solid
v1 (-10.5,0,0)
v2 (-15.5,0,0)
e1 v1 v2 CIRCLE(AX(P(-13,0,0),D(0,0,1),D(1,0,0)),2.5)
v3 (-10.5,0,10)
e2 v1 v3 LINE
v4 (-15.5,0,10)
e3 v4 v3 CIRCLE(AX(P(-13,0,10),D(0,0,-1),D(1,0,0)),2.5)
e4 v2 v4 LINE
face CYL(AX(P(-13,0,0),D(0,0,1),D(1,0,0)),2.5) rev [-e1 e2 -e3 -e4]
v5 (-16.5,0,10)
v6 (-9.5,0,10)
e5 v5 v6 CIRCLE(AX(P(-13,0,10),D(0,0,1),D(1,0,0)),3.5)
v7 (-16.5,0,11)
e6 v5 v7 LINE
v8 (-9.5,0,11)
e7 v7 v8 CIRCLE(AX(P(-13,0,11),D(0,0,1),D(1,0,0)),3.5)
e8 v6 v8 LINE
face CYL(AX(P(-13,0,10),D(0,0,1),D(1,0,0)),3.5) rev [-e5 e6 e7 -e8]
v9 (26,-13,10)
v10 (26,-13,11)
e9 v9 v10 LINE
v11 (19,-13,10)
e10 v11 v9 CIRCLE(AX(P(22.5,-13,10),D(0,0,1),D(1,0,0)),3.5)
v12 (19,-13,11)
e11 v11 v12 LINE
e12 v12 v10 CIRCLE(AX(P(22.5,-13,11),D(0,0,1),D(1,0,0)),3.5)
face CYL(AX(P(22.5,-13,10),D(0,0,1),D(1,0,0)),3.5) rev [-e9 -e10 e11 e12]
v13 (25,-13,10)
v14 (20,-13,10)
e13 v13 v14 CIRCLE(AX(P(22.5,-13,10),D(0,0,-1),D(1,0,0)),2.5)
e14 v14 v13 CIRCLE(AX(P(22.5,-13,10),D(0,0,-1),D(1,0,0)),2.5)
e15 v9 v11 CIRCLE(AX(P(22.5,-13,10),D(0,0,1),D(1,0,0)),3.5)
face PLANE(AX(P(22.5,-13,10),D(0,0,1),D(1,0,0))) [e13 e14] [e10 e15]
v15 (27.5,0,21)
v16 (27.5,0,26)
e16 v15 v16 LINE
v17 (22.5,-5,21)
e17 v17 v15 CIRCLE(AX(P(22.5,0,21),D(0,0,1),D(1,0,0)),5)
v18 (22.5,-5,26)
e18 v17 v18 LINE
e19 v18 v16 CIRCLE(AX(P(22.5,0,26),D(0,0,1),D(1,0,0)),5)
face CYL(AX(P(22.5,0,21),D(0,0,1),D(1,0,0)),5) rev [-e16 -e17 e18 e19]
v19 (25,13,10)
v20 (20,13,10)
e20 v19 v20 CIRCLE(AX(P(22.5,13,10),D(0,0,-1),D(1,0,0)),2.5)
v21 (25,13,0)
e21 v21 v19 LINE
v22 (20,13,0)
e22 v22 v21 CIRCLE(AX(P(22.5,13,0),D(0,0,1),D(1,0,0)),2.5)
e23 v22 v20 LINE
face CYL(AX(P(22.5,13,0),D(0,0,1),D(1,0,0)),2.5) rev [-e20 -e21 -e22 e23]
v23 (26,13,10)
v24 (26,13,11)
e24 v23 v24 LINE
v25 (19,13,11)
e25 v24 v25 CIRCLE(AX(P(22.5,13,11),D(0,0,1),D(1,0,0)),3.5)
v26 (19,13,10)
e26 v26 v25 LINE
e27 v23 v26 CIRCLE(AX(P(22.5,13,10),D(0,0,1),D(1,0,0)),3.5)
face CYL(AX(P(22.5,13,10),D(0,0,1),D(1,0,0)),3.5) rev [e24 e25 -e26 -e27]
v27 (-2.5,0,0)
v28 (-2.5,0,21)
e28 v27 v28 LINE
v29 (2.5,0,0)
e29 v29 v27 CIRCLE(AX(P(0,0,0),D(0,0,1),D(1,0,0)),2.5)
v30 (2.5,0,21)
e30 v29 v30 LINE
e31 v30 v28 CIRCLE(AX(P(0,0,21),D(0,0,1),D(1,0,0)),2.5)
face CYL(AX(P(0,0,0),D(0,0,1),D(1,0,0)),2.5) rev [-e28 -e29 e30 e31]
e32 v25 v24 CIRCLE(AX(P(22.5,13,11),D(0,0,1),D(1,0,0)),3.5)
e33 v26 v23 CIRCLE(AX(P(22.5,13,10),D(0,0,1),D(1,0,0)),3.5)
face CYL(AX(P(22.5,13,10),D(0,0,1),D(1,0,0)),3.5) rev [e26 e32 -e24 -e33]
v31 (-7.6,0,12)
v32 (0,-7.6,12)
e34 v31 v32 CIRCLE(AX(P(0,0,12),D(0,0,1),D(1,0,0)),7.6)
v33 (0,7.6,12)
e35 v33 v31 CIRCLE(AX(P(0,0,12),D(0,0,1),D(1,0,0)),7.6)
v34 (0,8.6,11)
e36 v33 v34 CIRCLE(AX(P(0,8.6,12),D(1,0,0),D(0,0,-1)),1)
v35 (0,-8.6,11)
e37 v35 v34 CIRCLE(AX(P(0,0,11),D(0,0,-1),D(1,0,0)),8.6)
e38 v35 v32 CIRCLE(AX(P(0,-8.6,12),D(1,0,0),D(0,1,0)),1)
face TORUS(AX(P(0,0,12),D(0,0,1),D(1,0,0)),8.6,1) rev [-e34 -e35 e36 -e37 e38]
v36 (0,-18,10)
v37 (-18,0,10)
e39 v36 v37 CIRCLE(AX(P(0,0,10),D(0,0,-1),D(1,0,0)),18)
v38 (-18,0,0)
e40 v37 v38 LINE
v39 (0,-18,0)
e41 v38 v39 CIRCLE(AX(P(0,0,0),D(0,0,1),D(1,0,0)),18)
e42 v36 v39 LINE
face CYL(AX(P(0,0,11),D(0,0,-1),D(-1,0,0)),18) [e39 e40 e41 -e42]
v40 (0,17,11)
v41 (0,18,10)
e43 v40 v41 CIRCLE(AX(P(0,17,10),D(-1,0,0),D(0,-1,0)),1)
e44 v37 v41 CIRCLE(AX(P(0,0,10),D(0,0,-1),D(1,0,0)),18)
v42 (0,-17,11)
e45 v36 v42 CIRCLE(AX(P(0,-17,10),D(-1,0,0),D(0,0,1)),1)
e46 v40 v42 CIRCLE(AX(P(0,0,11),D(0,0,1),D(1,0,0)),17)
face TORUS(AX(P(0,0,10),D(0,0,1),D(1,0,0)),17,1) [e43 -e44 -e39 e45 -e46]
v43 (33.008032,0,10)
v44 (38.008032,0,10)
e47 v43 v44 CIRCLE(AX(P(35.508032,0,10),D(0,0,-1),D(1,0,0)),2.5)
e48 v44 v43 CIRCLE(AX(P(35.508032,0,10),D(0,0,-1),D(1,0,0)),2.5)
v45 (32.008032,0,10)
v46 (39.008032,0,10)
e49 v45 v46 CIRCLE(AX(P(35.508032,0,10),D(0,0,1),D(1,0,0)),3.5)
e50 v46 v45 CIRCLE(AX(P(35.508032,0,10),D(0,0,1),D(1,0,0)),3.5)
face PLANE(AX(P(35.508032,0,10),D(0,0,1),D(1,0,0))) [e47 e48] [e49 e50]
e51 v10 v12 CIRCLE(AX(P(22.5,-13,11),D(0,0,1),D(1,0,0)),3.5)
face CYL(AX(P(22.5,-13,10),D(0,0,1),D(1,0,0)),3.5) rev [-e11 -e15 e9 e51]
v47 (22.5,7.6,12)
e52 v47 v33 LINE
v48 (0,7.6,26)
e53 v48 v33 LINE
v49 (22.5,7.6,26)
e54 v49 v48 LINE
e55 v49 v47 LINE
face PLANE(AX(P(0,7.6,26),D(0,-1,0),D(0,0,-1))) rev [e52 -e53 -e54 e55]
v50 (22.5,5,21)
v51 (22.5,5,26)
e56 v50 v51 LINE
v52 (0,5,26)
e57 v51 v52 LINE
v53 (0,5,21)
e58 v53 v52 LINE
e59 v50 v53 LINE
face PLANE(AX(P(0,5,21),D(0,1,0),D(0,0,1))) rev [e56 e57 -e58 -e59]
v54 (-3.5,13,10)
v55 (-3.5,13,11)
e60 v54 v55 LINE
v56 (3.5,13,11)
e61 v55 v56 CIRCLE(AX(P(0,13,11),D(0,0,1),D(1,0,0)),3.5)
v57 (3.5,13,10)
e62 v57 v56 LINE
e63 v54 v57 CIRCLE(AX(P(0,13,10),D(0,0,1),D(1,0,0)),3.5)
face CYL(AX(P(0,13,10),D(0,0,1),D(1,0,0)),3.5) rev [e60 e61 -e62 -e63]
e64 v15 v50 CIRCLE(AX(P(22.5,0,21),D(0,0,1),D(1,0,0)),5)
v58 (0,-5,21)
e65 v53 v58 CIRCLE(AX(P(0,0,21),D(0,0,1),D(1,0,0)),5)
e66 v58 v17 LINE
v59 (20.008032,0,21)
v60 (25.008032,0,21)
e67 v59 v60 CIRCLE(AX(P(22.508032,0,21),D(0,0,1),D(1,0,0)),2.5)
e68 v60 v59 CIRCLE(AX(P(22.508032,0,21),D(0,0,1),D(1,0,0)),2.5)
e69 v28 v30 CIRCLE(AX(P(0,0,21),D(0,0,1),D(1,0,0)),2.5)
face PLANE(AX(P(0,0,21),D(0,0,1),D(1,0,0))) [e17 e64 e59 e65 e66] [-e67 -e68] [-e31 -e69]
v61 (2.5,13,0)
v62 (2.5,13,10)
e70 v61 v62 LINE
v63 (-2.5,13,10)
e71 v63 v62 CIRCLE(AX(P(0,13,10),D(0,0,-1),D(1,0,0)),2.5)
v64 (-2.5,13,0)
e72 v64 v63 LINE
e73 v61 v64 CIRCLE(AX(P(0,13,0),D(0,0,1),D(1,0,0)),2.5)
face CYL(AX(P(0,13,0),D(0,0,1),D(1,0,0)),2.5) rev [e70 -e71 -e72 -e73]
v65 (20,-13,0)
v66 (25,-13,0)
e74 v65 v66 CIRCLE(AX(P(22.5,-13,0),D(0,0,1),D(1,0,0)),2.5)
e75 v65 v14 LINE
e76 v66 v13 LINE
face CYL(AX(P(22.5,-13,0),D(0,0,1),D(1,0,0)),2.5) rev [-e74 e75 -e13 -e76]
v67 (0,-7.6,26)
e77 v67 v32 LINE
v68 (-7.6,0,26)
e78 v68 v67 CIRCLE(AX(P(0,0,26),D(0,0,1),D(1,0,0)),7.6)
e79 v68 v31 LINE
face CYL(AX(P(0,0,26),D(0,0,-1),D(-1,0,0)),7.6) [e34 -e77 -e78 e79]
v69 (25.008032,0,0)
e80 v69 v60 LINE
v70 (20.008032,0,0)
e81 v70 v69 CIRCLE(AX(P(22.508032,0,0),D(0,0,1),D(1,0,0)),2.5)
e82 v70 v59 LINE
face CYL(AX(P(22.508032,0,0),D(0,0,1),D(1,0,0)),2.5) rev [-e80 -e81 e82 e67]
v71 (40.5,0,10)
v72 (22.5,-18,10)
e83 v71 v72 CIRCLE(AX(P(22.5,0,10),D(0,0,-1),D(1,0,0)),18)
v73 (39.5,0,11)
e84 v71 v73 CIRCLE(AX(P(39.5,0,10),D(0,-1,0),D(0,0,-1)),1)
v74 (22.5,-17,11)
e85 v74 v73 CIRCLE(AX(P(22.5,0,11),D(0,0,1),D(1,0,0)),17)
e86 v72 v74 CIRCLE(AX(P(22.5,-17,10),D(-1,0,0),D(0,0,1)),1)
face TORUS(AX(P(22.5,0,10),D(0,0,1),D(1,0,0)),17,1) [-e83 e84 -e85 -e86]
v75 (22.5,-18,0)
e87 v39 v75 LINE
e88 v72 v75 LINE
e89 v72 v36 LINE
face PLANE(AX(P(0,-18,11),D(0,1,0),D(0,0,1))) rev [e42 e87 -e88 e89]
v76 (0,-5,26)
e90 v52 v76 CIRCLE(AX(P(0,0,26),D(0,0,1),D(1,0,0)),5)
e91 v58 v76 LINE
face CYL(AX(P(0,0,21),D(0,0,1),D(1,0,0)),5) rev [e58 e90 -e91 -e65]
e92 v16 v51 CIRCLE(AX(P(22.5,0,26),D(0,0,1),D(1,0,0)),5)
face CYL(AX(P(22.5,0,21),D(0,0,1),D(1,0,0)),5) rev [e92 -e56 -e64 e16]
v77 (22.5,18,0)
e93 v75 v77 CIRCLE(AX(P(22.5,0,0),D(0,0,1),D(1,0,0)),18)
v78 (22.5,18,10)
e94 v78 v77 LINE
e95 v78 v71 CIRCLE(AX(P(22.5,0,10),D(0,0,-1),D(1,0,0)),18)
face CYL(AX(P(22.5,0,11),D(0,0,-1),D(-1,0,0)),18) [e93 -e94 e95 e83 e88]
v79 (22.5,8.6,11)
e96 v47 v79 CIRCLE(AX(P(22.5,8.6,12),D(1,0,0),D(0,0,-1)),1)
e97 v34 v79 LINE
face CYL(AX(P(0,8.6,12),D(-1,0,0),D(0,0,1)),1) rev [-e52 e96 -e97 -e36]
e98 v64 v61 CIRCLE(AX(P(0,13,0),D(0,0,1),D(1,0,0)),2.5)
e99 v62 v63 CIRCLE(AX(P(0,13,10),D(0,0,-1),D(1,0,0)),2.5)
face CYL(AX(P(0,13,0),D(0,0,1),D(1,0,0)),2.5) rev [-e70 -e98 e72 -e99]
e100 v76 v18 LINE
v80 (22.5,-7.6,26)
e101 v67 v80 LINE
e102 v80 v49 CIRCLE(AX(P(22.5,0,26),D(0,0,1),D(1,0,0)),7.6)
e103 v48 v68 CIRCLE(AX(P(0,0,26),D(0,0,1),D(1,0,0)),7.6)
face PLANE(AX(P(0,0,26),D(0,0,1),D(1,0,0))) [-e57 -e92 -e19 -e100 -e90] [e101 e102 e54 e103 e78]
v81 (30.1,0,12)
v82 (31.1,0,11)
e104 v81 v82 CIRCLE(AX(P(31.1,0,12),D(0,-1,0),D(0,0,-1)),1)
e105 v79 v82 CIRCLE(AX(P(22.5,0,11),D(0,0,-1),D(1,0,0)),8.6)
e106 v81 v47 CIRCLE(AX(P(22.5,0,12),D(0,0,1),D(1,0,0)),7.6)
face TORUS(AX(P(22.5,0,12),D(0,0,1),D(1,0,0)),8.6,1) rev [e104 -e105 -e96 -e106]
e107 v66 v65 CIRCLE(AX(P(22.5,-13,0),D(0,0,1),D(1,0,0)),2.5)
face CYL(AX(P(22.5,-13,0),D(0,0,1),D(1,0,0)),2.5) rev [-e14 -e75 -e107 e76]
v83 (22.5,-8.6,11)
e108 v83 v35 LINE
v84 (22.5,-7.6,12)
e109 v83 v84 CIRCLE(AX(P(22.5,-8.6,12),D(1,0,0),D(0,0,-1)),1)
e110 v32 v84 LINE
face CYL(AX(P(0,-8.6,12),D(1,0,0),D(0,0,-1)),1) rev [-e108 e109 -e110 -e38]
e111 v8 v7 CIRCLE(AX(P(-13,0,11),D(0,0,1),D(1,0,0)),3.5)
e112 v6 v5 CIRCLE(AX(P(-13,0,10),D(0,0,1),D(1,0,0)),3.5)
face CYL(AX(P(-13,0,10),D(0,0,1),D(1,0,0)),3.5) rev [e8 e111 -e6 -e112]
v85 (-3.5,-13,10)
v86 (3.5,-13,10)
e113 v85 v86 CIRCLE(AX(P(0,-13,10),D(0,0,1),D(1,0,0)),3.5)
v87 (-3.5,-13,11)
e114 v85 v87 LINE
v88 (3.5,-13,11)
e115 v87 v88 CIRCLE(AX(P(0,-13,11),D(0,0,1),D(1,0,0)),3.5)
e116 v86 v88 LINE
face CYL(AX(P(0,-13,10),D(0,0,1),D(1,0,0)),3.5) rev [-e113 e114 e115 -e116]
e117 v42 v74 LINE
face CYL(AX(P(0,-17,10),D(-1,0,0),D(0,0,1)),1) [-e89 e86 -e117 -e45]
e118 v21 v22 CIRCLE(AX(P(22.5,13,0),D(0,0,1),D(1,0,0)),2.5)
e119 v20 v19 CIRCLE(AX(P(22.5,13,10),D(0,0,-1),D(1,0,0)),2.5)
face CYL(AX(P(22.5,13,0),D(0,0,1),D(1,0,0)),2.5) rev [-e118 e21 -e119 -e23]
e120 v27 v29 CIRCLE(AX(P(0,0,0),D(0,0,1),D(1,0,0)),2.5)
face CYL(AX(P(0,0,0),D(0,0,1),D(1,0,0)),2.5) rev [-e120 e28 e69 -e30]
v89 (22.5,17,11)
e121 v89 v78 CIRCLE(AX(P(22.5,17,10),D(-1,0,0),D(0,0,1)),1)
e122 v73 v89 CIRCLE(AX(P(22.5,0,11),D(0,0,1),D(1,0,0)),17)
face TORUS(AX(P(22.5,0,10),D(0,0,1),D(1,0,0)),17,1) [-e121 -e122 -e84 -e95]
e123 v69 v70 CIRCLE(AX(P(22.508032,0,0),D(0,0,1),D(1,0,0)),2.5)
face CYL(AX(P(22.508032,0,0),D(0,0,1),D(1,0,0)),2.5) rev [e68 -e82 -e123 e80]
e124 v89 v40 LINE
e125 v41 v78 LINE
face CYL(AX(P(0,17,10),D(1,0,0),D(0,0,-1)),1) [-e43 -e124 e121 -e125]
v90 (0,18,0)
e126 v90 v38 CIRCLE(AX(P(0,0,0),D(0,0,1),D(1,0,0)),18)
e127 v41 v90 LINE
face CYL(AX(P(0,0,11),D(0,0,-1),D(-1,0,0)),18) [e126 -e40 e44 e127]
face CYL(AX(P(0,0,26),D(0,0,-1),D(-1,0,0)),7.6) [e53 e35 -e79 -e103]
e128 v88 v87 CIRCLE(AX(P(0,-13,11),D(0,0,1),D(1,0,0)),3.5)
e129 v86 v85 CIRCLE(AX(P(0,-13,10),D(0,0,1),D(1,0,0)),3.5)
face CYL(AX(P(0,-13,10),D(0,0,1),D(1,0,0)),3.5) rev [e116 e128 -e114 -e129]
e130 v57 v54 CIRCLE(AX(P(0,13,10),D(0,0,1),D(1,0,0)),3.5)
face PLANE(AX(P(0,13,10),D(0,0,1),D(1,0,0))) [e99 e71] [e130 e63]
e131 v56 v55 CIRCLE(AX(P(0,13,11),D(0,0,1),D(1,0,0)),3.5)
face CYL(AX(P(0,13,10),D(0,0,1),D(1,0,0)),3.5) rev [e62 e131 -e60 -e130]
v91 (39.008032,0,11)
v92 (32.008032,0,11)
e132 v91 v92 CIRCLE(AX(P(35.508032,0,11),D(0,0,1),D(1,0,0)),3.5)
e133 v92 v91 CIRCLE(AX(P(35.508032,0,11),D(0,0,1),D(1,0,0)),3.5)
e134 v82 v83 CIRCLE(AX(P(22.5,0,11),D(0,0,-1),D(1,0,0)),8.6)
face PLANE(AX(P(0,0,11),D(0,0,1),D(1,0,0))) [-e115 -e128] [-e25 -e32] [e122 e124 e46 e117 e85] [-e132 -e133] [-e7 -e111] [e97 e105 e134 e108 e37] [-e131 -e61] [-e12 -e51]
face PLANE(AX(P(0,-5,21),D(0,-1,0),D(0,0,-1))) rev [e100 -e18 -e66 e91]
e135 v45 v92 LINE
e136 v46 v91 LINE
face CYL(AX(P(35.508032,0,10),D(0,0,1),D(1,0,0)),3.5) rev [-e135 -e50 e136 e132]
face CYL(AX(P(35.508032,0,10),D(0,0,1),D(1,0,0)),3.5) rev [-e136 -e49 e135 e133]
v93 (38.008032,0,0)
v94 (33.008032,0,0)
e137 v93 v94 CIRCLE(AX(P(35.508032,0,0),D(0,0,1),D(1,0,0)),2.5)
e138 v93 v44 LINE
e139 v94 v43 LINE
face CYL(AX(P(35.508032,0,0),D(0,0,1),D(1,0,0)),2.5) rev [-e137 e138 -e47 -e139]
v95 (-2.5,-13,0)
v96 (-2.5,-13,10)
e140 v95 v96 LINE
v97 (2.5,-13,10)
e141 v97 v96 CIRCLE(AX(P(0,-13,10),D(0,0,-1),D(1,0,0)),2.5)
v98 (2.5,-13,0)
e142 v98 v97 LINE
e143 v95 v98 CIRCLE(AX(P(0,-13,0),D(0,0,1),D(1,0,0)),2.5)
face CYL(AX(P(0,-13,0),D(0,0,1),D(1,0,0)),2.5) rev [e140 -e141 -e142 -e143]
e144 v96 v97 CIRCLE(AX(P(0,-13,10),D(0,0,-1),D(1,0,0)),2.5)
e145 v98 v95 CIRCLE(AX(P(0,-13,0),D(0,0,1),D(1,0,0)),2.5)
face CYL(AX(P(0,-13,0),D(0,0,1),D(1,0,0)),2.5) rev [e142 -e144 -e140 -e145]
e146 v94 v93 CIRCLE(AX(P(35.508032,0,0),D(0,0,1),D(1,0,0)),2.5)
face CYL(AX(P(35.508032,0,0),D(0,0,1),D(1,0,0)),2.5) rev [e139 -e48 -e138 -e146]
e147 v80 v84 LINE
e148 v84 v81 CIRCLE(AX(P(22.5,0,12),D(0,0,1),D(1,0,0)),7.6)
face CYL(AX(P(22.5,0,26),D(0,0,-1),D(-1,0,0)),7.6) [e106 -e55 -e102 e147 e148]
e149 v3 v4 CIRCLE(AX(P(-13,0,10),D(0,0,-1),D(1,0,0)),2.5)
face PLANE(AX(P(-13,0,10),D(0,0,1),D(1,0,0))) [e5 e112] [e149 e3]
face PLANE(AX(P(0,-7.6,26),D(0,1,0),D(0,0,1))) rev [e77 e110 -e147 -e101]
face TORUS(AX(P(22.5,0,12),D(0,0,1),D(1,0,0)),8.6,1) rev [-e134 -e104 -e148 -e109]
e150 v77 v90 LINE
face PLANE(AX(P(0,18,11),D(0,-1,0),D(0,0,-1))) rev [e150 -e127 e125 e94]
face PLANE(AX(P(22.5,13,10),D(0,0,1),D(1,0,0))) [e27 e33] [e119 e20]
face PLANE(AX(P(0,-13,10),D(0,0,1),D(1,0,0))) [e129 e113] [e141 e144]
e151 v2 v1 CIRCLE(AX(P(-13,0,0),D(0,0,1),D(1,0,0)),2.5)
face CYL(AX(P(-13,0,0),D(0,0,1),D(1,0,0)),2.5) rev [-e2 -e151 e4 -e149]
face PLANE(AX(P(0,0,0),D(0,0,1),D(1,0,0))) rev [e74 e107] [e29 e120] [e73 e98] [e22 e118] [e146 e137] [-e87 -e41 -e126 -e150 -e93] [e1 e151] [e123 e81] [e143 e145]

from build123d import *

# Parameters (mm, degrees)
BASE_FLANGE_DEPTH          = 11
OBROUND_BOSS_DEPTH         = 15
BOSS_POCKET_DEPTH          = 5
MOUNTING_HOLES_A_PROFILE_R = 2.5
MOUNTING_HOLES_A_DEPTH     = 47.789421881
SPOT_FACES_A_PROFILE_R     = 3.5
SPOT_FACES_A_DEPTH         = 1
CENTRE_HOLES_PROFILE_R     = 2.5
CENTRE_HOLES_DEPTH         = 50.043348173
BOSS_ROOT_FILLET_R1_R      = 1
MOUNTING_HOLES_B_PROFILE_R = 2.5
MOUNTING_HOLES_B_DEPTH     = 47.789421881
SPOT_FACES_B_PROFILE_R     = 3.5
SPOT_FACES_B_DEPTH         = 1


with BuildPart() as part:
    # Flange Profile → Base Flange (new body)
    with BuildSketch(Plane.XY):
        with BuildLine():
            Line((0, 18), (22.5, 18))
            ThreePointArc((22.5, 18), (40.5, 0), (22.5, -18))
            Line((22.5, -18), (0, -18))
            ThreePointArc((0, -18), (-18, 0), (0, 18))
        make_face()
    extrude(amount=BASE_FLANGE_DEPTH)

    # Boss Profile → Obround Boss (add)
    with BuildSketch(Plane.XY.offset(11)):
        with BuildLine():
            Line((0, 7.6), (22.5, 7.6))
            ThreePointArc((22.5, 7.6), (30.1, 0), (22.5, -7.6))
            Line((22.5, -7.6), (0, -7.6))
            ThreePointArc((0, -7.6), (-7.6, 0), (0, 7.6))
        make_face()
    extrude(amount=OBROUND_BOSS_DEPTH)

    # Boss Pocket Profile → Boss Pocket (cut)
    with BuildSketch(Plane.XY.offset(26)):
        with BuildLine():
            Line((0, 5), (22.5, 5))
            ThreePointArc((22.5, 5), (27.5, 0), (22.5, -5))
            Line((22.5, -5), (0, -5))
            ThreePointArc((0, -5), (-5, 0), (0, 5))
        make_face()
    extrude(amount=-BOSS_POCKET_DEPTH, mode=Mode.SUBTRACT)

    # Mounting Holes A Profile → Mounting Holes A (cut, through all)
    with BuildSketch(Plane.XY.offset(11)):
        with Locations((0, 13)):
            Circle(MOUNTING_HOLES_A_PROFILE_R)
        with Locations((22.5, 13)):
            Circle(MOUNTING_HOLES_A_PROFILE_R)
        with Locations((0, -13)):
            Circle(MOUNTING_HOLES_A_PROFILE_R)
        with Locations((22.5, -13)):
            Circle(MOUNTING_HOLES_A_PROFILE_R)
    extrude(amount=-MOUNTING_HOLES_A_DEPTH, mode=Mode.SUBTRACT)

    # Spot Faces A Profile → Spot Faces A (cut)
    with BuildSketch(Plane.XY.offset(11)):
        with Locations((0, 13)):
            Circle(SPOT_FACES_A_PROFILE_R)
        with Locations((22.5, 13)):
            Circle(SPOT_FACES_A_PROFILE_R)
        with Locations((22.5, -13)):
            Circle(SPOT_FACES_A_PROFILE_R)
        with Locations((0, -13)):
            Circle(SPOT_FACES_A_PROFILE_R)
    extrude(amount=-SPOT_FACES_A_DEPTH, mode=Mode.SUBTRACT)

    # Centre Holes Profile → Centre Holes (cut, through all)
    with BuildSketch(Plane.XY.offset(21)):
        Circle(CENTRE_HOLES_PROFILE_R)
        with Locations((22.50803184, 0)):
            Circle(CENTRE_HOLES_PROFILE_R)
    extrude(amount=-CENTRE_HOLES_DEPTH, mode=Mode.SUBTRACT)

    # Boss Root Fillet R1
    boss_root_fillet_r1_edges = [part.edges().sort_by_distance(p)[0] for p in [
        (40.5, 0, 11),
        (-7.6, 0, 11),
        (11.25, -7.6, 11),
        (11.25, 18, 11),
        (30.1, 0, 11),
        (11.25, 7.6, 11),
        (-18, 0, 11),
        (11.25, -18, 11),
    ]]
    fillet(boss_root_fillet_r1_edges, radius=BOSS_ROOT_FILLET_R1_R)

    # Mounting Holes B Profile → Mounting Holes B (cut, through all)
    with BuildSketch(Plane.XY.offset(11)):
        with Locations((-13, 0)):
            Circle(MOUNTING_HOLES_B_PROFILE_R)
        with Locations((35.50803184, 0)):
            Circle(MOUNTING_HOLES_B_PROFILE_R)
    extrude(amount=-MOUNTING_HOLES_B_DEPTH, mode=Mode.SUBTRACT)

    # Spot Faces B Profile → Spot Faces B (cut)
    with BuildSketch(Plane.XY.offset(11)):
        with Locations((-13, 0)):
            Circle(SPOT_FACES_B_PROFILE_R)
        with Locations((35.50803184, 0)):
            Circle(SPOT_FACES_B_PROFILE_R)
    extrude(amount=-SPOT_FACES_B_DEPTH, mode=Mode.SUBTRACT)


solid = part.part
